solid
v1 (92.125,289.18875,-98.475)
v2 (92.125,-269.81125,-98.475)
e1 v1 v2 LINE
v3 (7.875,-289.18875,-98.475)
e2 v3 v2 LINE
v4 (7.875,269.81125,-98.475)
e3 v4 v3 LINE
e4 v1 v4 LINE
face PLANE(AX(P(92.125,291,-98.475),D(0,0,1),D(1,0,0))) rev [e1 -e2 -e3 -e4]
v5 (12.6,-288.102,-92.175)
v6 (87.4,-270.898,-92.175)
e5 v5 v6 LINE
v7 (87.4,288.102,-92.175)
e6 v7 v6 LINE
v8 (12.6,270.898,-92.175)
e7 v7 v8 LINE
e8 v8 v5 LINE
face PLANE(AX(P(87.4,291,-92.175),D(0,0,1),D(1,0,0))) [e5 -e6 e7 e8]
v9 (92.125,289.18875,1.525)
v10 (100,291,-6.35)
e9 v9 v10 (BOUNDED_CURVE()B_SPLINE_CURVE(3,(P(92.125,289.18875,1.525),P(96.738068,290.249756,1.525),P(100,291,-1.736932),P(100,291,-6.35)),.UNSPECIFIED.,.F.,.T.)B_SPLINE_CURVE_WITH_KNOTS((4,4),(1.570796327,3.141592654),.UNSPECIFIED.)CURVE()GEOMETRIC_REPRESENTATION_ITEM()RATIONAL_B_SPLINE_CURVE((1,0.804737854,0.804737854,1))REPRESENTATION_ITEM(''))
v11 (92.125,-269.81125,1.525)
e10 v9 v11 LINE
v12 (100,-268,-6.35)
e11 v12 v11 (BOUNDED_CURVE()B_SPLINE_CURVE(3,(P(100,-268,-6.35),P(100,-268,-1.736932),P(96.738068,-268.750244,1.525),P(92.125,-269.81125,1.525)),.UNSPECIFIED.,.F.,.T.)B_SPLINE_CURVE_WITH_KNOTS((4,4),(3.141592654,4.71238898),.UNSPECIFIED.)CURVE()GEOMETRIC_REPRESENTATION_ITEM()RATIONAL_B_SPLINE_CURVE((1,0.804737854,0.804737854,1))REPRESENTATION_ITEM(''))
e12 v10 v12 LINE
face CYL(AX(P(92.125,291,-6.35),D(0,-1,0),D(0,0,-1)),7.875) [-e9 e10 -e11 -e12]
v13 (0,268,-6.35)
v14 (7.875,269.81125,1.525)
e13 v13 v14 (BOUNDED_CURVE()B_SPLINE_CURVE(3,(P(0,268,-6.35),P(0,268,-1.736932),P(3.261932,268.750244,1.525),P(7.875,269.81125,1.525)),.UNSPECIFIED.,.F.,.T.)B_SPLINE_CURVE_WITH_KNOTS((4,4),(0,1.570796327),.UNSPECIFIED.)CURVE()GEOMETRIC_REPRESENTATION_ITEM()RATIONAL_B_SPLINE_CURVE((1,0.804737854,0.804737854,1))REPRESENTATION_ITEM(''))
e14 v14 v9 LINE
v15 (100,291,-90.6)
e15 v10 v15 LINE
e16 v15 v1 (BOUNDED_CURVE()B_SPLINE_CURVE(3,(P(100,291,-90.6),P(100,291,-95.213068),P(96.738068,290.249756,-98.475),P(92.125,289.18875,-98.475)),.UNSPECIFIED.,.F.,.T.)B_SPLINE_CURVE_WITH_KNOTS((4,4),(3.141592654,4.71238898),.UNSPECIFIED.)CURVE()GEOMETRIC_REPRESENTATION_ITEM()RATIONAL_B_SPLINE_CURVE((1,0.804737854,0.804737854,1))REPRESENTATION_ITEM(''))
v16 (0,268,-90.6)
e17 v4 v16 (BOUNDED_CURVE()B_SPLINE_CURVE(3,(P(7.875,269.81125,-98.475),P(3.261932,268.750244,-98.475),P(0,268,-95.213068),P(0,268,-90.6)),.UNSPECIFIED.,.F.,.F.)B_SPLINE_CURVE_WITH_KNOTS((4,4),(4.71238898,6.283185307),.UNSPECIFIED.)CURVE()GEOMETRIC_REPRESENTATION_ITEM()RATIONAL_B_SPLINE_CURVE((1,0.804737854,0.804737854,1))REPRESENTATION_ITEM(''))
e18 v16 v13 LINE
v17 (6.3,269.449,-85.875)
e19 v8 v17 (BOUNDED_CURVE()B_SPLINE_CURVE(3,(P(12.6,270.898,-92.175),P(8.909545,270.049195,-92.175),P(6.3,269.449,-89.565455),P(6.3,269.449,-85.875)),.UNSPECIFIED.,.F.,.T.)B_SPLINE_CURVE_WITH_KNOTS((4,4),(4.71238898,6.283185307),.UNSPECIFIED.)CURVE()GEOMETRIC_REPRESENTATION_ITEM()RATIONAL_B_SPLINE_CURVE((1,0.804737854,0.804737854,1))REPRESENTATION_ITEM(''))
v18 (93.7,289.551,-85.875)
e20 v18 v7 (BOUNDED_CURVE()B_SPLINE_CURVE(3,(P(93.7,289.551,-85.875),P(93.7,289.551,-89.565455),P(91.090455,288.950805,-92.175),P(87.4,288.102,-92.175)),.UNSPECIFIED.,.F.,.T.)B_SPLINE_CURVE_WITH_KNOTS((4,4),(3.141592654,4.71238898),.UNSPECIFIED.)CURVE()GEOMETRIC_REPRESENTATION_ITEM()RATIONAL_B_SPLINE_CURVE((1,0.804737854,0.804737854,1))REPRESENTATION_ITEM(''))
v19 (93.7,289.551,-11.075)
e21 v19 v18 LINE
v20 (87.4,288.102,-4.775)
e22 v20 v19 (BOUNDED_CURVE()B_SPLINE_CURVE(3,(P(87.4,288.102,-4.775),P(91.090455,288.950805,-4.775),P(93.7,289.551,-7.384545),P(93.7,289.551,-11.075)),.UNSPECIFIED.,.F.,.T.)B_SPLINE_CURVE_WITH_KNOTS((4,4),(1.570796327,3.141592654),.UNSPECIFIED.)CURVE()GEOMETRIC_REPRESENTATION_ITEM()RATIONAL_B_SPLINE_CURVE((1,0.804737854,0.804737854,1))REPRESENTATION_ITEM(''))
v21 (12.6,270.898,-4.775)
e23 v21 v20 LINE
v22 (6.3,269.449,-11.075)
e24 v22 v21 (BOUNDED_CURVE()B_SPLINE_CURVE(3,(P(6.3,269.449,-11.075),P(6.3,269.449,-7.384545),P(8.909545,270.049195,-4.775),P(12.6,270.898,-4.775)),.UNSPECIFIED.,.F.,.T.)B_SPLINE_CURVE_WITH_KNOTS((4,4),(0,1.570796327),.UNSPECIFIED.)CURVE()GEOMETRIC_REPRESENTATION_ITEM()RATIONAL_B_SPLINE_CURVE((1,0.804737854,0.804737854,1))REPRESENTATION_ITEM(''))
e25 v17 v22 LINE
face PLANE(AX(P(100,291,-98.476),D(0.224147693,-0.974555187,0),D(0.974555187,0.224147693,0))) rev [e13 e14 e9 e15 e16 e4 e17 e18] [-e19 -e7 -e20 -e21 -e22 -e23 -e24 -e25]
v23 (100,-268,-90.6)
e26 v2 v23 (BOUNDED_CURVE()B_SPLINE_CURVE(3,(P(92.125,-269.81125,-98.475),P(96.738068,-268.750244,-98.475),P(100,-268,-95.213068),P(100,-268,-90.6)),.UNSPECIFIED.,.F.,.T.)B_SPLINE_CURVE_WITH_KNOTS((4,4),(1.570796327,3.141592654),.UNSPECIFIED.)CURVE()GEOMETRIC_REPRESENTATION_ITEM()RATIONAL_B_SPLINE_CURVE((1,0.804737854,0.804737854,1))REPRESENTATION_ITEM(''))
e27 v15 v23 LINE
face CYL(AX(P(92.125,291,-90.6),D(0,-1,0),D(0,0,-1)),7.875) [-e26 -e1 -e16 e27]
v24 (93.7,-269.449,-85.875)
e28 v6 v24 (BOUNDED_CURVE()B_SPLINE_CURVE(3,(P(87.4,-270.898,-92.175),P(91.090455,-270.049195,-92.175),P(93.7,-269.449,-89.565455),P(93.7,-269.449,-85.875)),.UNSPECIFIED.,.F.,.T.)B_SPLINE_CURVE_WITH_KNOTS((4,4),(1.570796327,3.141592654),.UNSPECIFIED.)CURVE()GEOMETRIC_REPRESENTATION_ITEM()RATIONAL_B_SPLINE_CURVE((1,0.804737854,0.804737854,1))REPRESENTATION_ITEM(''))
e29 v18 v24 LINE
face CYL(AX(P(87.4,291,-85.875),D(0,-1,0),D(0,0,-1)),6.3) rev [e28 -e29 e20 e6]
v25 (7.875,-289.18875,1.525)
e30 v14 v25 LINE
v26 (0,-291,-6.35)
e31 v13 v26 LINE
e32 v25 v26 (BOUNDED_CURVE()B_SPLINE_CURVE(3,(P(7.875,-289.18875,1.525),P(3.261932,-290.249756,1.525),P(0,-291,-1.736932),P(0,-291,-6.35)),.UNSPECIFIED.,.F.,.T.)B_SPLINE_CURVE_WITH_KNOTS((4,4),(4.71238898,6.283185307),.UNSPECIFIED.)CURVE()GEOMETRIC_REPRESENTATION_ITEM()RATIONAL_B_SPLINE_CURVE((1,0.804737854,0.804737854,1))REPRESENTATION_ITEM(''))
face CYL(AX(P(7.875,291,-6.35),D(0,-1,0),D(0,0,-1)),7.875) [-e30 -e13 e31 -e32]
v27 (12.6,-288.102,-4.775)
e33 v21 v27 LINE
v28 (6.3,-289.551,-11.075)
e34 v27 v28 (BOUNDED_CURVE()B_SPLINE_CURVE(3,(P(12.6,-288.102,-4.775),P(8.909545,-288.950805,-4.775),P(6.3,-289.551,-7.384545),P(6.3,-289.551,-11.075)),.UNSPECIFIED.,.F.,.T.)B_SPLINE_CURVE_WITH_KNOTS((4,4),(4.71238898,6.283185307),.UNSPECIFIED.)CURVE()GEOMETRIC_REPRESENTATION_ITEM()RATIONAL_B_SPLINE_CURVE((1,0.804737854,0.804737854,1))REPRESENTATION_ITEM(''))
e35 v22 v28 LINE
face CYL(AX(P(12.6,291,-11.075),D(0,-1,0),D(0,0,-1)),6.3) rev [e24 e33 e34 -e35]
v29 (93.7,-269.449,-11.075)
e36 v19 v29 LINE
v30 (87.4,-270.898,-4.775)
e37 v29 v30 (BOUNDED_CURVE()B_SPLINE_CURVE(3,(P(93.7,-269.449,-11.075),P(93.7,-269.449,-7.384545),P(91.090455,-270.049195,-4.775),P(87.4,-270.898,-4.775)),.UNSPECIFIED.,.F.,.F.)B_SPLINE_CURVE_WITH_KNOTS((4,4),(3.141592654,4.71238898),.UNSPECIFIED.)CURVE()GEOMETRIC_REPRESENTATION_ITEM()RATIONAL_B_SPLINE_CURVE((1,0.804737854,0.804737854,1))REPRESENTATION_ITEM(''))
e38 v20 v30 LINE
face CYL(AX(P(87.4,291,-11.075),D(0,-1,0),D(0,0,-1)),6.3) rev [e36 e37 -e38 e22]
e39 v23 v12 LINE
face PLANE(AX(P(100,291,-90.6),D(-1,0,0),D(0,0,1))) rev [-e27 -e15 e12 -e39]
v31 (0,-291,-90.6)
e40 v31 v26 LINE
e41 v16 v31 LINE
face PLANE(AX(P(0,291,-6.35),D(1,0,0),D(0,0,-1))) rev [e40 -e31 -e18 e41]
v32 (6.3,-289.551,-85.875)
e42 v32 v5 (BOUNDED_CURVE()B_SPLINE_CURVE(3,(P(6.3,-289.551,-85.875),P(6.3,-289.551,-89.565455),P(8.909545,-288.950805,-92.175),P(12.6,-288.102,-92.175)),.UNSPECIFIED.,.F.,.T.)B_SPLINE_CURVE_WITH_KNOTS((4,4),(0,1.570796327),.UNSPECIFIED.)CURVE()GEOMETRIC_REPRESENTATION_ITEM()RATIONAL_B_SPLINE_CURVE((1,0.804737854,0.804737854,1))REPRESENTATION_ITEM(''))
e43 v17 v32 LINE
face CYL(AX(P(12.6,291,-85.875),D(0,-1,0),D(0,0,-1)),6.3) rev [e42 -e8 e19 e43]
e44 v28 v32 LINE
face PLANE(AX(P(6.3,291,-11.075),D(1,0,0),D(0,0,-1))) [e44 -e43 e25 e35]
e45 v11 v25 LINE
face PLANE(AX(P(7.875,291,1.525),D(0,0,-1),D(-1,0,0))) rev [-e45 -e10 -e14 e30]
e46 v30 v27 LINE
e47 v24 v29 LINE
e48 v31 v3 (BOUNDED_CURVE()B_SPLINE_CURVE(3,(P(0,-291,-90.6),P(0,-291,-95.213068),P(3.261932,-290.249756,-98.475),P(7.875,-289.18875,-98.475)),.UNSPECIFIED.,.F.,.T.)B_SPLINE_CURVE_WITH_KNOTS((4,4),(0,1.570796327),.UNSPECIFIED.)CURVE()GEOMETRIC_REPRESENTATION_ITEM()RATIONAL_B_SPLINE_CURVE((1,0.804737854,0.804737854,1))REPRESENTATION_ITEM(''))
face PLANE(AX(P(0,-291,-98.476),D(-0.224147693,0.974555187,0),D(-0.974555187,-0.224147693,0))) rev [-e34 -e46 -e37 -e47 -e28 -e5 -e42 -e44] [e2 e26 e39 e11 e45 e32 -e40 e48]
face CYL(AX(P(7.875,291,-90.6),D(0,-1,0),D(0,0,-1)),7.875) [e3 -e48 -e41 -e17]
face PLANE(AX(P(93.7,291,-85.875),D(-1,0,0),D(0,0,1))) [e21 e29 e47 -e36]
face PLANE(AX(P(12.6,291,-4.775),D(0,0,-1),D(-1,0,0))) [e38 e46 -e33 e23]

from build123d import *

# Parameters (mm, degrees)
BOSS_EXTRUDE1_DEPTH = 291
CUT_EXTRUDE1_REACH  = 325.544


with BuildPart() as part:
    # Sketch2 → Boss-Extrude1 (new, symmetric)
    with BuildSketch(Plane(origin=(0, 0, 0), x_dir=(1, 0, 0), z_dir=(0, 1, 0))):
        with BuildLine():
            Line((7.875, -1.525), (92.125, -1.525))
            ThreePointArc((92.125, -1.525), (97.693465902, 0.781534098), (100, 6.35))
            Line((100, 6.35), (100, 90.6))
            ThreePointArc((100, 90.6), (97.693465902, 96.168465902), (92.125, 98.475))
            Line((92.125, 98.475), (7.875, 98.475))
            ThreePointArc((7.875, 98.475), (2.306534098, 96.168465902), (0, 90.6))
            Line((0, 90.6), (0, 6.35))
            ThreePointArc((0, 6.35), (2.306534098, 0.781534098), (7.875, -1.525))
        make_face()
        with BuildLine():
            Line((12.6, 4.775), (87.4, 4.775))
            ThreePointArc((87.4, 4.775), (91.854772721, 6.620227279), (93.7, 11.075))
            Line((93.7, 11.075), (93.7, 85.875))
            ThreePointArc((93.7, 85.875), (91.854772721, 90.329772721), (87.4, 92.175))
            Line((87.4, 92.175), (12.6, 92.175))
            ThreePointArc((12.6, 92.175), (8.145227279, 90.329772721), (6.3, 85.875))
            Line((6.3, 85.875), (6.3, 11.075))
            ThreePointArc((6.3, 11.075), (8.145227279, 6.620227279), (12.6, 4.775))
        make_face(mode=Mode.SUBTRACT)
    extrude(amount=BOSS_EXTRUDE1_DEPTH, both=True)

    # Sketch4 → Cut-Extrude1 (cut, up to next)
    with BuildSketch(Plane.XY.offset(1.525), mode=Mode.PRIVATE) as cut_extrude1_sk1:
        Polygon((100, 291), (0, 268), (0, 291), align=None)
    cut_extrude1_tool1 = extrude(cut_extrude1_sk1.sketch, amount=-CUT_EXTRUDE1_REACH, mode=Mode.PRIVATE) & part.part
    # Sketch4 → Cut-Extrude1 (cut, up to next)
    with BuildSketch(Plane.XY.offset(1.525), mode=Mode.PRIVATE) as cut_extrude1_sk2:
        Polygon((0, -291), (100, -268), (100, -291), align=None)
    cut_extrude1_tool2 = extrude(cut_extrude1_sk2.sketch, amount=-CUT_EXTRUDE1_REACH, mode=Mode.PRIVATE) & part.part
    add(cut_extrude1_tool1.solids().sort_by_distance((33.333333, 283.333333, 1.525))[0], mode=Mode.SUBTRACT)
    add(cut_extrude1_tool2.solids().sort_by_distance((66.666667, -283.333333, 1.525))[0], mode=Mode.SUBTRACT)


solid = part.part
